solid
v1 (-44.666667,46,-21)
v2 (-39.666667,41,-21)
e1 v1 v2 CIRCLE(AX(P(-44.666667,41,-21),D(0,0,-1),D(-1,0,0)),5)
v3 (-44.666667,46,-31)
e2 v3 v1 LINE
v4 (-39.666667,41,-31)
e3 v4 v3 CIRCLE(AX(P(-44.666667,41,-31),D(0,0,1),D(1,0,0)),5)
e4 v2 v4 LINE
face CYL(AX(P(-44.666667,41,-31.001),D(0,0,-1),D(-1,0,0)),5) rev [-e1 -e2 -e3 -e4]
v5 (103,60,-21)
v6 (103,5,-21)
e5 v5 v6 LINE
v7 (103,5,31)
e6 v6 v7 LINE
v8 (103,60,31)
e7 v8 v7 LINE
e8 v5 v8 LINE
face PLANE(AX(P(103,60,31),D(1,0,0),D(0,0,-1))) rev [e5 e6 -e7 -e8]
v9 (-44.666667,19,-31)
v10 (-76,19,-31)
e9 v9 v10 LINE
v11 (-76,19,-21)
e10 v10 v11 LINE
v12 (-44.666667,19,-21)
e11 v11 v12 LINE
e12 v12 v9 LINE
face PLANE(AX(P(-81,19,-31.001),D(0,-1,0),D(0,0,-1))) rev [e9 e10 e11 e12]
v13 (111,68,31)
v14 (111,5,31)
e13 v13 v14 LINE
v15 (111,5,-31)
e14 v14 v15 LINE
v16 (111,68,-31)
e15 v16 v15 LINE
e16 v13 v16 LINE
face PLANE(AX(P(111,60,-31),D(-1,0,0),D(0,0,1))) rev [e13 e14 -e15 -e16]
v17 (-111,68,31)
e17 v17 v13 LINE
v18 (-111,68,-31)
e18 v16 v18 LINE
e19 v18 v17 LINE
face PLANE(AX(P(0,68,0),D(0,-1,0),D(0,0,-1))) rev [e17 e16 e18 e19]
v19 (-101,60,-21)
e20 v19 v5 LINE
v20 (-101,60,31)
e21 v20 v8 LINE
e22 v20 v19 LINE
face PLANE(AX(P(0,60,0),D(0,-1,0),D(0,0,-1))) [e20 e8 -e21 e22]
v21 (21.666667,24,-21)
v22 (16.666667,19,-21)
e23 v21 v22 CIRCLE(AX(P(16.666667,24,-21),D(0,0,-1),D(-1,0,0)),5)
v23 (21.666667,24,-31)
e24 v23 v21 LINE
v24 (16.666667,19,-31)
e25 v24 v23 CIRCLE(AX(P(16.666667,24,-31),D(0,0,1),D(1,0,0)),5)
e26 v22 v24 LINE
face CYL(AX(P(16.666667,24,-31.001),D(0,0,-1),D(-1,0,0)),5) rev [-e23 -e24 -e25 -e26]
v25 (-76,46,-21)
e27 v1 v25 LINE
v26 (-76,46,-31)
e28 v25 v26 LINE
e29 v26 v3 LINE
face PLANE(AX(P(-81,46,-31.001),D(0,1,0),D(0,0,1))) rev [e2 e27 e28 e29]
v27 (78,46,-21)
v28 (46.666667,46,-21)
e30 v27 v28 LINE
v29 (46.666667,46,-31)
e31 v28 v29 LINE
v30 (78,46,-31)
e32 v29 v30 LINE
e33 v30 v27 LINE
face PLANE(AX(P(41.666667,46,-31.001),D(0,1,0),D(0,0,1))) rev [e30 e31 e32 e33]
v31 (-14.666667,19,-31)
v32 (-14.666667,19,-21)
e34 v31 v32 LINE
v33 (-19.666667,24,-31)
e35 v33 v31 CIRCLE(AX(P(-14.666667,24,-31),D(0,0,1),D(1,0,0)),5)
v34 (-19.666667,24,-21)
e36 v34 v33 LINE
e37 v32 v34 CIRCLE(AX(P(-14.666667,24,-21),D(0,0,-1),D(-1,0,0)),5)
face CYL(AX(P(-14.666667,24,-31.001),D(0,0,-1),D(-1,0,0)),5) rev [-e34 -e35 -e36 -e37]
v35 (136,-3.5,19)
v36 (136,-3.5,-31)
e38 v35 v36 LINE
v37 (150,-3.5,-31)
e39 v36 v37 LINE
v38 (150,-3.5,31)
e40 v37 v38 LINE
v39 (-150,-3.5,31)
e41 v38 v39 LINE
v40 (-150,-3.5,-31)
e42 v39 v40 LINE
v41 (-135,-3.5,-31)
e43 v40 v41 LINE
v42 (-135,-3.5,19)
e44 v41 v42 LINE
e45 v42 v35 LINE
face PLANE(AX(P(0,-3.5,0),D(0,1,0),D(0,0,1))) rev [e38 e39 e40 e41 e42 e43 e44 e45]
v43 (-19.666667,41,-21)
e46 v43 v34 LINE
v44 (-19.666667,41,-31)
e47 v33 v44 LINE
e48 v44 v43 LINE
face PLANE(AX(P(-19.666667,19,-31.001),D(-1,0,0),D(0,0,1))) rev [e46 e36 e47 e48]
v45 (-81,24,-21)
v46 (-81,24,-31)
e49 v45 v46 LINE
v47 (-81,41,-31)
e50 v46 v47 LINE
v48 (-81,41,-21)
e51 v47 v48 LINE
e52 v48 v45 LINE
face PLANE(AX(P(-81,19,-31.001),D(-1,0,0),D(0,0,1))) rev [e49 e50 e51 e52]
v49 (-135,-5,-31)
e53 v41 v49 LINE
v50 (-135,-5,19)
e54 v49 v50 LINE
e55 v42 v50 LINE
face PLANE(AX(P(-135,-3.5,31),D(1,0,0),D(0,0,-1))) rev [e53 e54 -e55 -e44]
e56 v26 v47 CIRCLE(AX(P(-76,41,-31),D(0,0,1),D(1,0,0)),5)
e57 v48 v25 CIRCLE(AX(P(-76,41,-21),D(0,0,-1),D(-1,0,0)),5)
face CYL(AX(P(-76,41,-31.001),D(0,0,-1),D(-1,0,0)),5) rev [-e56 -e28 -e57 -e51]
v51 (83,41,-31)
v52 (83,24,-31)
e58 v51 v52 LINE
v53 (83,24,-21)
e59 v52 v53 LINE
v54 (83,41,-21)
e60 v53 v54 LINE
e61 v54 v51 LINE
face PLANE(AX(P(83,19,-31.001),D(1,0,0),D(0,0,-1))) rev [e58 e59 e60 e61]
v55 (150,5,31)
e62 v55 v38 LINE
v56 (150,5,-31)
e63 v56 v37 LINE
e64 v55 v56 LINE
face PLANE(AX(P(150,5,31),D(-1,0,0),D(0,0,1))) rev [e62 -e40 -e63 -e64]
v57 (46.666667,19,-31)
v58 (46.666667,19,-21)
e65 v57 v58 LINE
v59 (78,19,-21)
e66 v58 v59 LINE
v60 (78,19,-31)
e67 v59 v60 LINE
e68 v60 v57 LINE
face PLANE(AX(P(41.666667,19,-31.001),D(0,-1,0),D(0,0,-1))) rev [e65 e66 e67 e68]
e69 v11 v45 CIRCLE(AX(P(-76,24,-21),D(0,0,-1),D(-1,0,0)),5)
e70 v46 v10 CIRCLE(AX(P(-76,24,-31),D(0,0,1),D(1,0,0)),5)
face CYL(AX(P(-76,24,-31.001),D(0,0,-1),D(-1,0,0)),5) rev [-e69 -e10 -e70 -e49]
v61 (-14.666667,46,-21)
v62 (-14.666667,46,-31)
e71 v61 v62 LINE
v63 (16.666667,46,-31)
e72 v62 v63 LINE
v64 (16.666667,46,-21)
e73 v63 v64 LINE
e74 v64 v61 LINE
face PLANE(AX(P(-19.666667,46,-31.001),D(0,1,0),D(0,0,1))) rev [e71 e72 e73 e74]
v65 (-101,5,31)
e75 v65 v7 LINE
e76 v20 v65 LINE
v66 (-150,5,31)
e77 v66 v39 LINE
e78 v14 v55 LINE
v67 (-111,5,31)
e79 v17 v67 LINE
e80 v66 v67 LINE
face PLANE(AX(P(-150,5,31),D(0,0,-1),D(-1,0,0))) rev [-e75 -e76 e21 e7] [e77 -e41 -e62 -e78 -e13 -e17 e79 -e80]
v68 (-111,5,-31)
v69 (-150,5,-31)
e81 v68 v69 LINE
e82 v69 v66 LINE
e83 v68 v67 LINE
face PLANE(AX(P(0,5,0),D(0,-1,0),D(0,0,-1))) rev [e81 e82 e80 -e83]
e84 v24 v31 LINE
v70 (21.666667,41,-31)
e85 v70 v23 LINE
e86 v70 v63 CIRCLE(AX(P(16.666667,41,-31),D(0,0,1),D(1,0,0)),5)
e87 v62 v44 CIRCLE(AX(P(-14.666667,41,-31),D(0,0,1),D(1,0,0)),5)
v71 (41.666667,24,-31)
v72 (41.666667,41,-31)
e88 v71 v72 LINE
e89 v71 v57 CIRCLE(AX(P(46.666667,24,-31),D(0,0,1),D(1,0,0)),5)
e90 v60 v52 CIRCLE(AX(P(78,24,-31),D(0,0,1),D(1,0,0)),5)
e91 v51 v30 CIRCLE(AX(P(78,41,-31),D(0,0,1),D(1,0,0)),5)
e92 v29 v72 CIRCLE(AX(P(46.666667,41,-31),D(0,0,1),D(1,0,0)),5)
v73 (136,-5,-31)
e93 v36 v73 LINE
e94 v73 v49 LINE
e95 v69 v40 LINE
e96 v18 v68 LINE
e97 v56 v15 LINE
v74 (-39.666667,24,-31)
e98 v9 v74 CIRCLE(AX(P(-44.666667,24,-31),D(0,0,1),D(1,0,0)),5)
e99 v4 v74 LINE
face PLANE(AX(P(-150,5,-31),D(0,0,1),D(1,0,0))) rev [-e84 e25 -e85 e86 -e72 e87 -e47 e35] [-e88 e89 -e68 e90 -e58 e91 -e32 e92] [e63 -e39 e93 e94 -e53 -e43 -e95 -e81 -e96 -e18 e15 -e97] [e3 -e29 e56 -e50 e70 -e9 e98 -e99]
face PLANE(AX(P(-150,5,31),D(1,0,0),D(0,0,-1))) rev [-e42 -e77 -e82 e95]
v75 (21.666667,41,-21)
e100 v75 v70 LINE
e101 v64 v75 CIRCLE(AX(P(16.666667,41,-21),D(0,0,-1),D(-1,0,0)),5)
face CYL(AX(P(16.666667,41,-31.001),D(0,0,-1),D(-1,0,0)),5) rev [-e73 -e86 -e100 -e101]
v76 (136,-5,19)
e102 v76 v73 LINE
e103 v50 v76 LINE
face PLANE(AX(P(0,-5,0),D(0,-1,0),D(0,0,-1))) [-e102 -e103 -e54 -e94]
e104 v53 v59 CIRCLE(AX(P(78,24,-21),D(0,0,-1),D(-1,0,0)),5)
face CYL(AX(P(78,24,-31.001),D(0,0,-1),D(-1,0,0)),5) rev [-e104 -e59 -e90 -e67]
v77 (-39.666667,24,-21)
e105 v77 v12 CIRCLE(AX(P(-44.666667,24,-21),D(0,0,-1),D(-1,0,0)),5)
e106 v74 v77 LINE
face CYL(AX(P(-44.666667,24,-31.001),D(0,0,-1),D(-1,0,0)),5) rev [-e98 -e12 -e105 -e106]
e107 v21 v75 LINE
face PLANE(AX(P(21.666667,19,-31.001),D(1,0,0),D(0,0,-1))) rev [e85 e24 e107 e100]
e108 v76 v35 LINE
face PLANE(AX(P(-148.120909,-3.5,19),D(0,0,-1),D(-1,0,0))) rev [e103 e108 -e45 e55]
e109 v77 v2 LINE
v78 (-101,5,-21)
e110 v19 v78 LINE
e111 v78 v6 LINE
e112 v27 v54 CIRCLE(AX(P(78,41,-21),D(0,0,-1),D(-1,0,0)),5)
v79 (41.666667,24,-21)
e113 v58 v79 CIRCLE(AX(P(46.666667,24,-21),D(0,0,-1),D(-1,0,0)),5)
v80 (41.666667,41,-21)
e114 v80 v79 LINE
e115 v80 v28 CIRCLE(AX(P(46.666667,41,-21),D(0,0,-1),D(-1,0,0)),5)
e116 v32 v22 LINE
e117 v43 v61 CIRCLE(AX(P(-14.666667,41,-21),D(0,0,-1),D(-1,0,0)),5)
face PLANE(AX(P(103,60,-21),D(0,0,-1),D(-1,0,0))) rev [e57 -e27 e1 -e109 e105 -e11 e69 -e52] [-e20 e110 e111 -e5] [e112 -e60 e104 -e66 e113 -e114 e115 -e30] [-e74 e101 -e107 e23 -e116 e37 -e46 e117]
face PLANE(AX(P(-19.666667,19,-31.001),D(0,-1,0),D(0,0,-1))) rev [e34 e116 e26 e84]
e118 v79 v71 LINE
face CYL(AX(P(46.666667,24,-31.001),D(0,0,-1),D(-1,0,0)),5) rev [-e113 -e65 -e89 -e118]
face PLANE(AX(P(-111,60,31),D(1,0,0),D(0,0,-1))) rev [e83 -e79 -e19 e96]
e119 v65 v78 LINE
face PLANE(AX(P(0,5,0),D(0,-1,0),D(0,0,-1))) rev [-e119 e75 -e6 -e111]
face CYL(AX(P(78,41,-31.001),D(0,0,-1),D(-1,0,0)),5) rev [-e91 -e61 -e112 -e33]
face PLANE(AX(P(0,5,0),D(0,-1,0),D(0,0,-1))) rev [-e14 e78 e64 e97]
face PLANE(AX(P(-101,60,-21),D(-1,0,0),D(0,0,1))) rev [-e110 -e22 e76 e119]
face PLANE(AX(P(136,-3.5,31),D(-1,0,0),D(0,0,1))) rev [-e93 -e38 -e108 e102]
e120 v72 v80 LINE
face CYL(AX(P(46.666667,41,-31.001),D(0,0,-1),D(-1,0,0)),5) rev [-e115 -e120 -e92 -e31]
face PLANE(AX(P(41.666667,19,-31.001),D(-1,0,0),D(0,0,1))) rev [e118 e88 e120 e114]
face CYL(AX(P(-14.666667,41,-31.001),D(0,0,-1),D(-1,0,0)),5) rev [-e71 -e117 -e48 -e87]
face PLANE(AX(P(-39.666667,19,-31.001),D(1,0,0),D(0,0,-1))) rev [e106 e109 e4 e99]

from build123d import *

# Parameters (mm, degrees)
SKETCH_1_W          = 300
SKETCH_1_H          = 62
EXTRUDE_1_DEPTH     = 5
SKETCH_2_W          = 298.120909486
SKETCH_2_H          = 12
CUT_EXTRUDE_1_DEPTH = 1.5
SKETCH_3_W          = 15
SKETCH_3_H          = 62
SKETCH_3_W_2        = 14
CUT_EXTRUDE_2_DEPTH = 1.5
EXTRUDE_2_DEPTH     = 55
SKETCH_5_W          = 222
SKETCH_5_H          = 62
EXTRUDE_3_DEPTH     = 8
CUT_EXTRUDE_3_REACH = 174.708
SKETCH_6_W          = 41.333333333
SKETCH_6_H          = 27
SKETCH_6_W_2        = 41.333333334
FILLET_1_R          = 5


with BuildPart() as part:
    # 草图1 → 凸台-拉伸1 (new, symmetric)
    with BuildSketch(Plane(origin=(0, 0, 0), x_dir=(1, 0, 0), z_dir=(0, 1, 0))):
        Rectangle(SKETCH_1_W, SKETCH_1_H)
    extrude(amount=EXTRUDE_1_DEPTH, both=True)

    # 草图2 → 切除-拉伸1 (cut)
    with BuildSketch(Plane.XZ.offset(5)):
        with Locations((0.939545257, 25)):
            Rectangle(SKETCH_2_W, SKETCH_2_H)
    extrude(amount=-CUT_EXTRUDE_1_DEPTH, mode=Mode.SUBTRACT)

    # 草图3 → 切除-拉伸2 (cut)
    with BuildSketch(Plane.XZ.offset(5)):
        with Locations((-142.5, 0)):
            Rectangle(SKETCH_3_W, SKETCH_3_H)
        with Locations((143, 0)):
            Rectangle(SKETCH_3_W_2, SKETCH_3_H)
    extrude(amount=-CUT_EXTRUDE_2_DEPTH, mode=Mode.SUBTRACT)

    # 草图4 → 凸台-拉伸2 (add)
    with BuildSketch(Plane(origin=(0, 5, 0), x_dir=(1, 0, 0), z_dir=(0, 1, 0))):
        Polygon((-111, -31), (-111, 31), (111, 31), (111, -31), (103, -31), (103, 21), (-101, 21), (-101, -31), align=None)
    extrude(amount=EXTRUDE_2_DEPTH)

    # 草图5 → 凸台-拉伸3 (add)
    with BuildSketch(Plane(origin=(0, 60, 0), x_dir=(1, 0, 0), z_dir=(0, 1, 0))):
        Rectangle(SKETCH_5_W, SKETCH_5_H)
    extrude(amount=EXTRUDE_3_DEPTH)

    # 草图6 → 切除-拉伸3 (cut, up to next)
    with BuildSketch(Plane.XY.offset(-21), mode=Mode.PRIVATE) as cut_extrude_3_sk1:
        with Locations((-60.333333334, 32.5)):
            Rectangle(SKETCH_6_W, SKETCH_6_H)
    cut_extrude_3_tool1 = extrude(cut_extrude_3_sk1.sketch, amount=-CUT_EXTRUDE_3_REACH, mode=Mode.PRIVATE) & part.part
    # 草图6 → 切除-拉伸3 (cut, up to next)
    with BuildSketch(Plane.XY.offset(-21), mode=Mode.PRIVATE) as cut_extrude_3_sk2:
        with Locations((62.333333334, 32.5)):
            Rectangle(SKETCH_6_W, SKETCH_6_H)
    cut_extrude_3_tool2 = extrude(cut_extrude_3_sk2.sketch, amount=-CUT_EXTRUDE_3_REACH, mode=Mode.PRIVATE) & part.part
    # 草图6 → 切除-拉伸3 (cut, up to next)
    with BuildSketch(Plane.XY.offset(-21), mode=Mode.PRIVATE) as cut_extrude_3_sk3:
        with Locations((1, 32.5)):
            Rectangle(SKETCH_6_W_2, SKETCH_6_H)
    cut_extrude_3_tool3 = extrude(cut_extrude_3_sk3.sketch, amount=-CUT_EXTRUDE_3_REACH, mode=Mode.PRIVATE) & part.part
    add(cut_extrude_3_tool1.solids().sort_by_distance((-60.333333, 32.5, -21))[0], mode=Mode.SUBTRACT)
    add(cut_extrude_3_tool2.solids().sort_by_distance((62.333333, 32.5, -21))[0], mode=Mode.SUBTRACT)
    add(cut_extrude_3_tool3.solids().sort_by_distance((1, 32.5, -21))[0], mode=Mode.SUBTRACT)

    # 圆角1
    fillet_1_edges = [part.edges().sort_by_distance(p)[0] for p in [
        (-39.666666667, 46, -26),
        (-39.666666667, 19, -26),
        (-81, 19, -26),
        (-81, 46, -26),
        (83, 46, -26),
        (83, 19, -26),
        (41.666666667, 19, -26),
        (41.666666667, 46, -26),
        (21.666666667, 46, -26),
        (21.666666667, 19, -26),
        (-19.666666667, 19, -26),
        (-19.666666667, 46, -26),
    ]]
    fillet(fillet_1_edges, radius=FILLET_1_R)


solid = part.part
